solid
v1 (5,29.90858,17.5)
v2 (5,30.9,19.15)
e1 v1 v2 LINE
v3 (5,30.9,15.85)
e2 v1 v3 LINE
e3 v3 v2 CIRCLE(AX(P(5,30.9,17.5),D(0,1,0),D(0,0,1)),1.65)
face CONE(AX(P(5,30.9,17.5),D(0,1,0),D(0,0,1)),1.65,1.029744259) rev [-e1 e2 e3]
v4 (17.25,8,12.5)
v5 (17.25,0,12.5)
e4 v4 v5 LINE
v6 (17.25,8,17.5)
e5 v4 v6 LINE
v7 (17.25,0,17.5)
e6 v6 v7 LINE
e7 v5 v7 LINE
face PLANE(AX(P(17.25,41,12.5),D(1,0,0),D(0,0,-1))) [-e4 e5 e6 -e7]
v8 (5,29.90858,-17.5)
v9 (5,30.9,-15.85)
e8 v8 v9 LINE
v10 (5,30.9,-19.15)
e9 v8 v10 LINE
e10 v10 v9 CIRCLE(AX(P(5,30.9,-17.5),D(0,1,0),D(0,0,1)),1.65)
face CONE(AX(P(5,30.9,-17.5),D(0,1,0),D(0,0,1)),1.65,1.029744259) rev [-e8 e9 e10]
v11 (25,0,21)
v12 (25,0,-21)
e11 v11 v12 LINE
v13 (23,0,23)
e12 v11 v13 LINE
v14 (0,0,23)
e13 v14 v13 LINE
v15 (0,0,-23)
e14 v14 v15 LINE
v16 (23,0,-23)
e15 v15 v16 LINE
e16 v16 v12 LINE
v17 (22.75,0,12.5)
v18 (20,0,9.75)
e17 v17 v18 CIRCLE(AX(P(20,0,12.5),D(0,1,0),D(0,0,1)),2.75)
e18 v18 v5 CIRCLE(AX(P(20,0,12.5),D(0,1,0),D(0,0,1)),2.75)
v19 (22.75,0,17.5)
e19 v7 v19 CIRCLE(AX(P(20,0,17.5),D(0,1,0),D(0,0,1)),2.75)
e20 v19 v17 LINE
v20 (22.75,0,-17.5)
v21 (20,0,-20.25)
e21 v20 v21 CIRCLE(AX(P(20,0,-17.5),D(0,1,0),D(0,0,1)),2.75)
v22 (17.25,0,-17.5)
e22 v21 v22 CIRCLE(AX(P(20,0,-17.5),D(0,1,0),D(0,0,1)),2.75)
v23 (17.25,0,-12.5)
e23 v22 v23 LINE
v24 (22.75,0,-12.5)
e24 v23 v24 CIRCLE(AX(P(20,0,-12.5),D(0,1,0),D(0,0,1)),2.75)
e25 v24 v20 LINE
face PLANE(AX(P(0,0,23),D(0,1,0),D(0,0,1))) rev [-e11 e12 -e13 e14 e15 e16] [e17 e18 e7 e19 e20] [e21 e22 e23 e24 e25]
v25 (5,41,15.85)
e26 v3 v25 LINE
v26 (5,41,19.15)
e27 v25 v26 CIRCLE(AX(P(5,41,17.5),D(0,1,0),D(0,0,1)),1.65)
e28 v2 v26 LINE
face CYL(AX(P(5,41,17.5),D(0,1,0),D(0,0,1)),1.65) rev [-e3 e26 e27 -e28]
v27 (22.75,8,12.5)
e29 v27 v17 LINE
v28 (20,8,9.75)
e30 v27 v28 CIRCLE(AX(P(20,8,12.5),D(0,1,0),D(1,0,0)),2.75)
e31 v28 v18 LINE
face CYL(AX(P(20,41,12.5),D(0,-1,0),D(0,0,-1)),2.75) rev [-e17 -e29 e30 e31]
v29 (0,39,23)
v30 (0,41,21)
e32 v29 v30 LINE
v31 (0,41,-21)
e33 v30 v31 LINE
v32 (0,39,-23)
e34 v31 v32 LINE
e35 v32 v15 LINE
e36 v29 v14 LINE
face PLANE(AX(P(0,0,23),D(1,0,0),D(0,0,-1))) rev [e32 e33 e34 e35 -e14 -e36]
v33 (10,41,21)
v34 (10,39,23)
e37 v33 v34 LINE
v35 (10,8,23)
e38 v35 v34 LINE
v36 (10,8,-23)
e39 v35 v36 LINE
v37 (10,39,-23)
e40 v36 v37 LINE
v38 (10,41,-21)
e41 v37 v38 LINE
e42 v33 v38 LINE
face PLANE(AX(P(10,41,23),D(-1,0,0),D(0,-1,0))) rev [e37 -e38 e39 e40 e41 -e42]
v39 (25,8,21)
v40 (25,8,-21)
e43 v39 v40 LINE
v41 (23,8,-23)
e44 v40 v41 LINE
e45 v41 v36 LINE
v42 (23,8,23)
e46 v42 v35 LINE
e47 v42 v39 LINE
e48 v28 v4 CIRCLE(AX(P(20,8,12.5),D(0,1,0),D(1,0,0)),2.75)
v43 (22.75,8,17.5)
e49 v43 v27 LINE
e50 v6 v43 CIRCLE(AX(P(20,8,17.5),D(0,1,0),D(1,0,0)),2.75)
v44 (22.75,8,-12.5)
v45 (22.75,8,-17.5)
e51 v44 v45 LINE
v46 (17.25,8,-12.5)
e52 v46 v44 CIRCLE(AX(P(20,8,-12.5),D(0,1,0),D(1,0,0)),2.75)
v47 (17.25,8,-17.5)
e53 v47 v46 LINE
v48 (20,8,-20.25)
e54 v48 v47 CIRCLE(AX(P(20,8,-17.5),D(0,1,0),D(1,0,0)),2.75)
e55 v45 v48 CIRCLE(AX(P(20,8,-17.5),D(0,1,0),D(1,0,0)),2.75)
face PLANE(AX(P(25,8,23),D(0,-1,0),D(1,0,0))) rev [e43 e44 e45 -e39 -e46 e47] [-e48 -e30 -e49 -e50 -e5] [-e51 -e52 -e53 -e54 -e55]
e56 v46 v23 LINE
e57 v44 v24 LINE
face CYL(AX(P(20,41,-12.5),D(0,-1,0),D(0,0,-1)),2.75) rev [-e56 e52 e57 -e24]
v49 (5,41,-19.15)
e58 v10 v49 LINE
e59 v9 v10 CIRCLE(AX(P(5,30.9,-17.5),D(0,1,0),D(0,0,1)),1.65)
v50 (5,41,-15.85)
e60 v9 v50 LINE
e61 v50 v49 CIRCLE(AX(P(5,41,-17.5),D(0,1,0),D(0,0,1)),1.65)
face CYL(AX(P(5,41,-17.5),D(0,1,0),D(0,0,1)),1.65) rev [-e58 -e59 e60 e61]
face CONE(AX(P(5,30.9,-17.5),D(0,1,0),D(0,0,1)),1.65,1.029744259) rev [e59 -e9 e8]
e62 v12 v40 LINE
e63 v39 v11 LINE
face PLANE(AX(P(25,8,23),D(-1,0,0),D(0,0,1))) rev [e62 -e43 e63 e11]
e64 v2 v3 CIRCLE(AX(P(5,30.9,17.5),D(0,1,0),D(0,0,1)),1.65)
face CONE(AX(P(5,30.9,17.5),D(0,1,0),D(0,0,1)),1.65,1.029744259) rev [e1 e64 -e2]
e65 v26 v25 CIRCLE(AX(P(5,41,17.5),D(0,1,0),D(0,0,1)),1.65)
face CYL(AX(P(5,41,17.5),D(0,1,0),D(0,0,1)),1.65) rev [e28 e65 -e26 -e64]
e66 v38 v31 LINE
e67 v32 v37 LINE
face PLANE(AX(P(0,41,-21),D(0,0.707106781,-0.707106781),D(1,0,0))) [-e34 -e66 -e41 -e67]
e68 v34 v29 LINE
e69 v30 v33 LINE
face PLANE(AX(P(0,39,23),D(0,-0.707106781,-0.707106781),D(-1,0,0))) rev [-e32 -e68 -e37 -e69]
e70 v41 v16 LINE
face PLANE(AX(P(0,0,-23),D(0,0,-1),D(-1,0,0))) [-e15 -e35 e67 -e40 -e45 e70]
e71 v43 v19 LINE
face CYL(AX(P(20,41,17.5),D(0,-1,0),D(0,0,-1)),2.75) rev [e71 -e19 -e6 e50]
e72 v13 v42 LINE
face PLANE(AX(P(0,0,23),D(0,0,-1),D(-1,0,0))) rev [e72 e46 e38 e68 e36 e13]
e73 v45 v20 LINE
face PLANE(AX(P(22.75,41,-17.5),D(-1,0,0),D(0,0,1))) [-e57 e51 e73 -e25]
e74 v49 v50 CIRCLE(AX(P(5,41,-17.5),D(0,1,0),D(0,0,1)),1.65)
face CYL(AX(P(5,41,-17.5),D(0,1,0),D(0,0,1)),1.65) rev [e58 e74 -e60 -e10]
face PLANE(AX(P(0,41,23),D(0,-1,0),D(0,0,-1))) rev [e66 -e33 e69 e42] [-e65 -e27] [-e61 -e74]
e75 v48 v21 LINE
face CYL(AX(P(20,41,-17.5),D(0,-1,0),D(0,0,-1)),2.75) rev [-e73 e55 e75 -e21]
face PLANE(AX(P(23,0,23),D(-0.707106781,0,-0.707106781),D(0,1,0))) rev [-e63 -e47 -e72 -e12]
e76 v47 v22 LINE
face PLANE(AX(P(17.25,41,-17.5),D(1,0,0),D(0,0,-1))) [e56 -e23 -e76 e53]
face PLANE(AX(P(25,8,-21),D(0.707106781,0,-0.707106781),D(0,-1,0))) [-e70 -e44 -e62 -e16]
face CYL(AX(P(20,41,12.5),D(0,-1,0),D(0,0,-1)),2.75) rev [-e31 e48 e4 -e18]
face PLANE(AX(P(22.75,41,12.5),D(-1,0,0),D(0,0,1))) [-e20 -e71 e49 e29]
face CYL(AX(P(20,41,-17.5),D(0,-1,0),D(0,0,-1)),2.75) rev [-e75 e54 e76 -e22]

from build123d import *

# Parameters (mm, degrees)
BOSS_EXTRUDE1_DEPTH   = 23
CUT_EXTRUDE1_DEPTH    = 54.244718048
M4_TAPPED_HOLE1_D     = 3.3
M4_TAPPED_HOLE1_DEPTH = 10.1
M4_TAPPED_HOLE1_TIP   = 0.991420021
CHAMFER4_SIZE         = 2


with BuildPart() as part:
    # Sketch1 → Boss-Extrude1 (new, symmetric)
    with BuildSketch(Plane.XY):
        Polygon((0, 41), (10, 41), (10, 8), (25, 8), (25, 0), (0, 0), align=None)
    extrude(amount=BOSS_EXTRUDE1_DEPTH, both=True)

    # Sketch2 → Cut-Extrude1 (cut, through all)
    with BuildSketch(Plane(origin=(0, 0, 0), x_dir=(1, 0, 0), z_dir=(0, 1, 0))):
        with BuildLine():
            Line((22.75, 17.5), (22.75, 12.5))
            ThreePointArc((22.75, 12.5), (20, 9.75), (17.25, 12.5))
            Line((17.25, 12.5), (17.25, 17.5))
            ThreePointArc((17.25, 17.5), (20, 20.25), (22.75, 17.5))
        make_face()
        with BuildLine():
            Line((22.75, -12.5), (22.75, -17.5))
            ThreePointArc((22.75, -17.5), (20, -20.25), (17.25, -17.5))
            Line((17.25, -17.5), (17.25, -12.5))
            ThreePointArc((17.25, -12.5), (20, -9.75), (22.75, -12.5))
        make_face()
    extrude(amount=CUT_EXTRUDE1_DEPTH, mode=Mode.SUBTRACT)

    # M4 Tapped Hole1
    with Locations(Plane(origin=(0, 41, 0), x_dir=(1, 0, 0), z_dir=(0, 1, 0))):
        with Locations((5, 17.5), (5, -17.5)):
            Hole(M4_TAPPED_HOLE1_D / 2, depth=M4_TAPPED_HOLE1_DEPTH)
            with Locations((0, 0, -(M4_TAPPED_HOLE1_DEPTH + M4_TAPPED_HOLE1_TIP / 2))):  # 118° drill point
                Cone(0, M4_TAPPED_HOLE1_D / 2, M4_TAPPED_HOLE1_TIP, mode=Mode.SUBTRACT)

    # Chamfer4
    chamfer4_edges = [part.edges().sort_by_distance(p)[0] for p in [
        (25, 4, 23),
        (5, 41, 23),
        (5, 41, -23),
        (25, 4, -23),
    ]]
    chamfer(chamfer4_edges, length=CHAMFER4_SIZE)


solid = part.part
